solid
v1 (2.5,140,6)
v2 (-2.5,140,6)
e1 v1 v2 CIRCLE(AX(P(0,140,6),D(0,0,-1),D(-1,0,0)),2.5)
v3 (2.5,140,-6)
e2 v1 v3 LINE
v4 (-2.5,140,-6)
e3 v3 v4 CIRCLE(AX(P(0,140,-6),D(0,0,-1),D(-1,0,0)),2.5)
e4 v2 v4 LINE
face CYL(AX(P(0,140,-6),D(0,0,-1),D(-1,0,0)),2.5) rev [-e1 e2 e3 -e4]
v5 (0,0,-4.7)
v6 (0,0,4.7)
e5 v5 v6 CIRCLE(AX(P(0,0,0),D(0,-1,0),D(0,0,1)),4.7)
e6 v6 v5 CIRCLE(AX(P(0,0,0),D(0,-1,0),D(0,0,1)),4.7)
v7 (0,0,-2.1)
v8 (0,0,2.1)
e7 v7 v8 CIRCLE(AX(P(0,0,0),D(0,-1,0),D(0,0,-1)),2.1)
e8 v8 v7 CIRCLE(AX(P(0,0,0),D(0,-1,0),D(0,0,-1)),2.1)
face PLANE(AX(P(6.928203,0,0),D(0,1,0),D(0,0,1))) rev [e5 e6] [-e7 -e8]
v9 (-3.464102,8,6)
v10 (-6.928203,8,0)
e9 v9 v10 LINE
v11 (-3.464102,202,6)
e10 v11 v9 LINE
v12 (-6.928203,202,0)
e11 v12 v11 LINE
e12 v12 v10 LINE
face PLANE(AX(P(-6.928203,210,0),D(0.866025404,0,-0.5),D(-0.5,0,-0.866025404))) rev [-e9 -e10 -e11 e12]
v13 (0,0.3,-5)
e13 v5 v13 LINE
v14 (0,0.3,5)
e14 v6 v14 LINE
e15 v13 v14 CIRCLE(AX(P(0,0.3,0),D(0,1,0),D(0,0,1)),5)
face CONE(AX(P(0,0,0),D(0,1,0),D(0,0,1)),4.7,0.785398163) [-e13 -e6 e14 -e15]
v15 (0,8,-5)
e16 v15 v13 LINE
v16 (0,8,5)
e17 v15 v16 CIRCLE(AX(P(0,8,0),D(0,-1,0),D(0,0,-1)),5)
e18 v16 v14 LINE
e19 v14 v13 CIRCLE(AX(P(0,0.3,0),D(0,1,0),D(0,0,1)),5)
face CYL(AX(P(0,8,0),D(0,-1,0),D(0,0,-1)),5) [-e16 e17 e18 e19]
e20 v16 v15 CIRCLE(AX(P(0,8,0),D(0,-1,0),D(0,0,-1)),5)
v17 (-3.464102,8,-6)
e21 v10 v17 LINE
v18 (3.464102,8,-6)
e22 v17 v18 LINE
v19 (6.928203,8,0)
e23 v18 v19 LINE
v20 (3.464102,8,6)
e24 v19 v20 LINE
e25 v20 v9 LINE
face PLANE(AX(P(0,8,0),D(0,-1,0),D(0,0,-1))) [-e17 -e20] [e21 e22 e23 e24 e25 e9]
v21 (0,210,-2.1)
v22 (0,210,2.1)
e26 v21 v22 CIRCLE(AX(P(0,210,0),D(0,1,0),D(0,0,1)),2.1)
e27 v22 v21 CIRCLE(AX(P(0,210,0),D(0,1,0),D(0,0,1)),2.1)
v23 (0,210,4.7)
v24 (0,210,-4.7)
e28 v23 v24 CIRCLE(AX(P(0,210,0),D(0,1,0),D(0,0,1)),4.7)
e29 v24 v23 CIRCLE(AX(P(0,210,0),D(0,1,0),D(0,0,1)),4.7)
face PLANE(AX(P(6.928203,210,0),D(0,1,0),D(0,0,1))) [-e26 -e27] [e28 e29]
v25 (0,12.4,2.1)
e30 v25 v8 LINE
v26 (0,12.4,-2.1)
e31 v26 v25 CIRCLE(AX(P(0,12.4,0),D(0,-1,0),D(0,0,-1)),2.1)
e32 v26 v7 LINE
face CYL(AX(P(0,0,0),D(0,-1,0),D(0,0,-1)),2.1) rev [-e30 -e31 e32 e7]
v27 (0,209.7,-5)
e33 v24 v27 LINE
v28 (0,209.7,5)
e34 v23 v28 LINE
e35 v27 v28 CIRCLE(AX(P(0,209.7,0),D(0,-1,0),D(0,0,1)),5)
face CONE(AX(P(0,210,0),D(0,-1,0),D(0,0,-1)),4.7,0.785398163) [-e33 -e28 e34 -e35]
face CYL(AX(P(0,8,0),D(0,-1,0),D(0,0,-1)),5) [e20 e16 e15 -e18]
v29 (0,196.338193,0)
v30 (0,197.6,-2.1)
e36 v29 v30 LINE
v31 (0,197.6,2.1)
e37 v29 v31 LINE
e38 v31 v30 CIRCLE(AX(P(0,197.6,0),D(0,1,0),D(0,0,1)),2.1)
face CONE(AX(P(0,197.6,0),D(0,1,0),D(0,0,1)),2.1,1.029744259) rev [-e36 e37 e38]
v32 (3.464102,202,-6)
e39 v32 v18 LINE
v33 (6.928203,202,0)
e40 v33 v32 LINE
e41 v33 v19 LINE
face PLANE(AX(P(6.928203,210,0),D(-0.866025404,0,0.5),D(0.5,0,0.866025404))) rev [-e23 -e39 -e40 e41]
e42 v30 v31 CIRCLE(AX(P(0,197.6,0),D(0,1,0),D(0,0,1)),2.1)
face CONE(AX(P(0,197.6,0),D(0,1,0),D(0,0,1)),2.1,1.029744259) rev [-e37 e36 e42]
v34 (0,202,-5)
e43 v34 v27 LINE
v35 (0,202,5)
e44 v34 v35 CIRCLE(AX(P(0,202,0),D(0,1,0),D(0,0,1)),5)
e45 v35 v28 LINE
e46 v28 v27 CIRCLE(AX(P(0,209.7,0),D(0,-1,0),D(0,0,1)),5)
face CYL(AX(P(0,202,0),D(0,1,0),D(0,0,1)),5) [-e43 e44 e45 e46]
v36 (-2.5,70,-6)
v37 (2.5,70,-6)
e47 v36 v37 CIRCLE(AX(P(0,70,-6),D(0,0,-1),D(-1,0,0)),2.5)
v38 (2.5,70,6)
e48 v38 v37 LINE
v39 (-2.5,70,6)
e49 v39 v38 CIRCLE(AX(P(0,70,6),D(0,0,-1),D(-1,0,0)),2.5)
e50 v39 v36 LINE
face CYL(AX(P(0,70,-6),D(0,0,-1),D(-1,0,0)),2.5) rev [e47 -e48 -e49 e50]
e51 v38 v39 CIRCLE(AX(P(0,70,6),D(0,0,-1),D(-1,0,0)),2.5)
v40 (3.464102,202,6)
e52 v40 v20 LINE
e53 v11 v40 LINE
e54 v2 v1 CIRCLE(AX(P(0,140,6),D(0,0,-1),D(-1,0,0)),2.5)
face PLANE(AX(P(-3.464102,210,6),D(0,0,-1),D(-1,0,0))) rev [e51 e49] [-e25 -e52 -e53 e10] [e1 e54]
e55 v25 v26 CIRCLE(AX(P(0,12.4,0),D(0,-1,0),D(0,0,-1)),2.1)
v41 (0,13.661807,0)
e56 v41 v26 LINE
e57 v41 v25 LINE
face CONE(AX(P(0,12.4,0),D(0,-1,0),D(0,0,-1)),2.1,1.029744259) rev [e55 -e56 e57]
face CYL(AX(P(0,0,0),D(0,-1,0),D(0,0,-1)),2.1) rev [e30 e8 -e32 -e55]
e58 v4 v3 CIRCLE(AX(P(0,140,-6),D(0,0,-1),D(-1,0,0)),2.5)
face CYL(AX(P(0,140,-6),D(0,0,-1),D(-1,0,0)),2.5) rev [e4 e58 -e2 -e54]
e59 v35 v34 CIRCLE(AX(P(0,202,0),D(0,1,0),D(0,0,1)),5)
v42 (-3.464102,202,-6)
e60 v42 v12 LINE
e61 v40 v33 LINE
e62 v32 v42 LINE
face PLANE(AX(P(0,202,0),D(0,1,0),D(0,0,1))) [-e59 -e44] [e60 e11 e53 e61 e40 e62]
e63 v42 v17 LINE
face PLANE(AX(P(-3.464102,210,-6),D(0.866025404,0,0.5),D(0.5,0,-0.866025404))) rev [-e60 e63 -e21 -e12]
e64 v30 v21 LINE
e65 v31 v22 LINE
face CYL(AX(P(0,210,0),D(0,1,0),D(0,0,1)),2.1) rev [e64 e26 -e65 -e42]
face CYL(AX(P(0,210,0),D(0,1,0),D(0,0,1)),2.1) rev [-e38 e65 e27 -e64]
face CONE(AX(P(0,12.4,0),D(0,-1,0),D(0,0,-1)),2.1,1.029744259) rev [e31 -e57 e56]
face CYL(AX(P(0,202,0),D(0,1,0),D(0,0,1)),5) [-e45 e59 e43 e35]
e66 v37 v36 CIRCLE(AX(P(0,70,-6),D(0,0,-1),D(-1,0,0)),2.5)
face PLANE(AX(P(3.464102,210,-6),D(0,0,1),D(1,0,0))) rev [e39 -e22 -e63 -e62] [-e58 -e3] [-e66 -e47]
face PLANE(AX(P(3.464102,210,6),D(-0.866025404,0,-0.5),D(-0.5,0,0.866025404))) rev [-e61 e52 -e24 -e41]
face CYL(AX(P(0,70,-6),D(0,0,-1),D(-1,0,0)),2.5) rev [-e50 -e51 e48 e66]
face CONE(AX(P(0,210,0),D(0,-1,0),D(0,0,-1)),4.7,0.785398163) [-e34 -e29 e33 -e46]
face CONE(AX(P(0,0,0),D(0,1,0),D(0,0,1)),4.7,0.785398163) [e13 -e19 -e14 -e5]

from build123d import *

# Parameters (mm, degrees)
BOSS_EXTRUDE1_DEPTH   = 210
SKETCH2_OUTSIDE_W     = 58.016
SKETCH2_OUTSIDE_H     = 56.16
SKETCH2_OUTSIDE_R     = 5
CUT_EXTRUDE1_DEPTH    = 8
SKETCH3_OUTSIDE_W     = 58.016
SKETCH3_OUTSIDE_H     = 56.16
SKETCH3_OUTSIDE_R     = 5
CUT_EXTRUDE2_DEPTH    = 8
M6_TAPPED_HOLE1_D     = 5
M5_TAPPED_HOLE1_D     = 4.2
M5_TAPPED_HOLE1_DEPTH = 12.4
M5_TAPPED_HOLE1_TIP   = 1.2618073
M5_TAPPED_HOLE2_D     = 4.2
M5_TAPPED_HOLE2_DEPTH = 12.4
M5_TAPPED_HOLE2_TIP   = 1.2618073
CHAMFER1_SIZE         = 0.3


with BuildPart() as part:
    # Sketch1 → Boss-Extrude1 (new body)
    with BuildSketch(Plane(origin=(0, 0, 0), x_dir=(1, 0, 0), z_dir=(0, 1, 0))):
        Polygon((6.92820323, 0), (3.464101615, 6), (-3.464101615, 6), (-6.92820323, 0), (-3.464101615, -6), (3.464101615, -6), align=None)
    extrude(amount=BOSS_EXTRUDE1_DEPTH)

    # Sketch2 outside → Cut-Extrude1 (cut)
    with BuildSketch(Plane(origin=(0, 210, 0), x_dir=(1, 0, 0), z_dir=(0, 1, 0))):
        Rectangle(SKETCH2_OUTSIDE_W, SKETCH2_OUTSIDE_H)
        with Locations(Location((0, 0, 0), (0, 0, 270))):
            Circle(SKETCH2_OUTSIDE_R, mode=Mode.SUBTRACT)
    extrude(amount=-CUT_EXTRUDE1_DEPTH, mode=Mode.SUBTRACT)

    # Sketch3 outside → Cut-Extrude2 (cut)
    with BuildSketch(Plane.XZ):
        Rectangle(SKETCH3_OUTSIDE_W, SKETCH3_OUTSIDE_H)
        with Locations(Location((0, 0, 0), (0, 0, 90))):
            Circle(SKETCH3_OUTSIDE_R, mode=Mode.SUBTRACT)
    extrude(amount=-CUT_EXTRUDE2_DEPTH, mode=Mode.SUBTRACT)

    # M6 Tapped Hole1 (through all)
    with Locations(Plane(origin=(0, 0, -6), x_dir=(-1, 0, 0), z_dir=(0, 0, -1))):
        with Locations((0, 140), (0, 70)):
            Hole(M6_TAPPED_HOLE1_D / 2)

    # M5 Tapped Hole1
    with Locations(Plane.XZ):
        with Locations((0, 0)):
            Hole(M5_TAPPED_HOLE1_D / 2, depth=M5_TAPPED_HOLE1_DEPTH)
            with Locations((0, 0, -(M5_TAPPED_HOLE1_DEPTH + M5_TAPPED_HOLE1_TIP / 2))):  # 118° drill point
                Cone(0, M5_TAPPED_HOLE1_D / 2, M5_TAPPED_HOLE1_TIP, mode=Mode.SUBTRACT)

    # M5 Tapped Hole2
    with Locations(Plane(origin=(0, 210, 0), x_dir=(-1, 0, 0), z_dir=(0, 1, 0))):
        with Locations((0, 0)):
            Hole(M5_TAPPED_HOLE2_D / 2, depth=M5_TAPPED_HOLE2_DEPTH)
            with Locations((0, 0, -(M5_TAPPED_HOLE2_DEPTH + M5_TAPPED_HOLE2_TIP / 2))):  # 118° drill point
                Cone(0, M5_TAPPED_HOLE2_D / 2, M5_TAPPED_HOLE2_TIP, mode=Mode.SUBTRACT)

    # Chamfer1
    chamfer1_edges = [part.edges().sort_by_distance(p)[0] for p in [
        (0, 210, -5),
        (0, 0, -5),
    ]]
    chamfer(chamfer1_edges, length=CHAMFER1_SIZE)


solid = part.part
